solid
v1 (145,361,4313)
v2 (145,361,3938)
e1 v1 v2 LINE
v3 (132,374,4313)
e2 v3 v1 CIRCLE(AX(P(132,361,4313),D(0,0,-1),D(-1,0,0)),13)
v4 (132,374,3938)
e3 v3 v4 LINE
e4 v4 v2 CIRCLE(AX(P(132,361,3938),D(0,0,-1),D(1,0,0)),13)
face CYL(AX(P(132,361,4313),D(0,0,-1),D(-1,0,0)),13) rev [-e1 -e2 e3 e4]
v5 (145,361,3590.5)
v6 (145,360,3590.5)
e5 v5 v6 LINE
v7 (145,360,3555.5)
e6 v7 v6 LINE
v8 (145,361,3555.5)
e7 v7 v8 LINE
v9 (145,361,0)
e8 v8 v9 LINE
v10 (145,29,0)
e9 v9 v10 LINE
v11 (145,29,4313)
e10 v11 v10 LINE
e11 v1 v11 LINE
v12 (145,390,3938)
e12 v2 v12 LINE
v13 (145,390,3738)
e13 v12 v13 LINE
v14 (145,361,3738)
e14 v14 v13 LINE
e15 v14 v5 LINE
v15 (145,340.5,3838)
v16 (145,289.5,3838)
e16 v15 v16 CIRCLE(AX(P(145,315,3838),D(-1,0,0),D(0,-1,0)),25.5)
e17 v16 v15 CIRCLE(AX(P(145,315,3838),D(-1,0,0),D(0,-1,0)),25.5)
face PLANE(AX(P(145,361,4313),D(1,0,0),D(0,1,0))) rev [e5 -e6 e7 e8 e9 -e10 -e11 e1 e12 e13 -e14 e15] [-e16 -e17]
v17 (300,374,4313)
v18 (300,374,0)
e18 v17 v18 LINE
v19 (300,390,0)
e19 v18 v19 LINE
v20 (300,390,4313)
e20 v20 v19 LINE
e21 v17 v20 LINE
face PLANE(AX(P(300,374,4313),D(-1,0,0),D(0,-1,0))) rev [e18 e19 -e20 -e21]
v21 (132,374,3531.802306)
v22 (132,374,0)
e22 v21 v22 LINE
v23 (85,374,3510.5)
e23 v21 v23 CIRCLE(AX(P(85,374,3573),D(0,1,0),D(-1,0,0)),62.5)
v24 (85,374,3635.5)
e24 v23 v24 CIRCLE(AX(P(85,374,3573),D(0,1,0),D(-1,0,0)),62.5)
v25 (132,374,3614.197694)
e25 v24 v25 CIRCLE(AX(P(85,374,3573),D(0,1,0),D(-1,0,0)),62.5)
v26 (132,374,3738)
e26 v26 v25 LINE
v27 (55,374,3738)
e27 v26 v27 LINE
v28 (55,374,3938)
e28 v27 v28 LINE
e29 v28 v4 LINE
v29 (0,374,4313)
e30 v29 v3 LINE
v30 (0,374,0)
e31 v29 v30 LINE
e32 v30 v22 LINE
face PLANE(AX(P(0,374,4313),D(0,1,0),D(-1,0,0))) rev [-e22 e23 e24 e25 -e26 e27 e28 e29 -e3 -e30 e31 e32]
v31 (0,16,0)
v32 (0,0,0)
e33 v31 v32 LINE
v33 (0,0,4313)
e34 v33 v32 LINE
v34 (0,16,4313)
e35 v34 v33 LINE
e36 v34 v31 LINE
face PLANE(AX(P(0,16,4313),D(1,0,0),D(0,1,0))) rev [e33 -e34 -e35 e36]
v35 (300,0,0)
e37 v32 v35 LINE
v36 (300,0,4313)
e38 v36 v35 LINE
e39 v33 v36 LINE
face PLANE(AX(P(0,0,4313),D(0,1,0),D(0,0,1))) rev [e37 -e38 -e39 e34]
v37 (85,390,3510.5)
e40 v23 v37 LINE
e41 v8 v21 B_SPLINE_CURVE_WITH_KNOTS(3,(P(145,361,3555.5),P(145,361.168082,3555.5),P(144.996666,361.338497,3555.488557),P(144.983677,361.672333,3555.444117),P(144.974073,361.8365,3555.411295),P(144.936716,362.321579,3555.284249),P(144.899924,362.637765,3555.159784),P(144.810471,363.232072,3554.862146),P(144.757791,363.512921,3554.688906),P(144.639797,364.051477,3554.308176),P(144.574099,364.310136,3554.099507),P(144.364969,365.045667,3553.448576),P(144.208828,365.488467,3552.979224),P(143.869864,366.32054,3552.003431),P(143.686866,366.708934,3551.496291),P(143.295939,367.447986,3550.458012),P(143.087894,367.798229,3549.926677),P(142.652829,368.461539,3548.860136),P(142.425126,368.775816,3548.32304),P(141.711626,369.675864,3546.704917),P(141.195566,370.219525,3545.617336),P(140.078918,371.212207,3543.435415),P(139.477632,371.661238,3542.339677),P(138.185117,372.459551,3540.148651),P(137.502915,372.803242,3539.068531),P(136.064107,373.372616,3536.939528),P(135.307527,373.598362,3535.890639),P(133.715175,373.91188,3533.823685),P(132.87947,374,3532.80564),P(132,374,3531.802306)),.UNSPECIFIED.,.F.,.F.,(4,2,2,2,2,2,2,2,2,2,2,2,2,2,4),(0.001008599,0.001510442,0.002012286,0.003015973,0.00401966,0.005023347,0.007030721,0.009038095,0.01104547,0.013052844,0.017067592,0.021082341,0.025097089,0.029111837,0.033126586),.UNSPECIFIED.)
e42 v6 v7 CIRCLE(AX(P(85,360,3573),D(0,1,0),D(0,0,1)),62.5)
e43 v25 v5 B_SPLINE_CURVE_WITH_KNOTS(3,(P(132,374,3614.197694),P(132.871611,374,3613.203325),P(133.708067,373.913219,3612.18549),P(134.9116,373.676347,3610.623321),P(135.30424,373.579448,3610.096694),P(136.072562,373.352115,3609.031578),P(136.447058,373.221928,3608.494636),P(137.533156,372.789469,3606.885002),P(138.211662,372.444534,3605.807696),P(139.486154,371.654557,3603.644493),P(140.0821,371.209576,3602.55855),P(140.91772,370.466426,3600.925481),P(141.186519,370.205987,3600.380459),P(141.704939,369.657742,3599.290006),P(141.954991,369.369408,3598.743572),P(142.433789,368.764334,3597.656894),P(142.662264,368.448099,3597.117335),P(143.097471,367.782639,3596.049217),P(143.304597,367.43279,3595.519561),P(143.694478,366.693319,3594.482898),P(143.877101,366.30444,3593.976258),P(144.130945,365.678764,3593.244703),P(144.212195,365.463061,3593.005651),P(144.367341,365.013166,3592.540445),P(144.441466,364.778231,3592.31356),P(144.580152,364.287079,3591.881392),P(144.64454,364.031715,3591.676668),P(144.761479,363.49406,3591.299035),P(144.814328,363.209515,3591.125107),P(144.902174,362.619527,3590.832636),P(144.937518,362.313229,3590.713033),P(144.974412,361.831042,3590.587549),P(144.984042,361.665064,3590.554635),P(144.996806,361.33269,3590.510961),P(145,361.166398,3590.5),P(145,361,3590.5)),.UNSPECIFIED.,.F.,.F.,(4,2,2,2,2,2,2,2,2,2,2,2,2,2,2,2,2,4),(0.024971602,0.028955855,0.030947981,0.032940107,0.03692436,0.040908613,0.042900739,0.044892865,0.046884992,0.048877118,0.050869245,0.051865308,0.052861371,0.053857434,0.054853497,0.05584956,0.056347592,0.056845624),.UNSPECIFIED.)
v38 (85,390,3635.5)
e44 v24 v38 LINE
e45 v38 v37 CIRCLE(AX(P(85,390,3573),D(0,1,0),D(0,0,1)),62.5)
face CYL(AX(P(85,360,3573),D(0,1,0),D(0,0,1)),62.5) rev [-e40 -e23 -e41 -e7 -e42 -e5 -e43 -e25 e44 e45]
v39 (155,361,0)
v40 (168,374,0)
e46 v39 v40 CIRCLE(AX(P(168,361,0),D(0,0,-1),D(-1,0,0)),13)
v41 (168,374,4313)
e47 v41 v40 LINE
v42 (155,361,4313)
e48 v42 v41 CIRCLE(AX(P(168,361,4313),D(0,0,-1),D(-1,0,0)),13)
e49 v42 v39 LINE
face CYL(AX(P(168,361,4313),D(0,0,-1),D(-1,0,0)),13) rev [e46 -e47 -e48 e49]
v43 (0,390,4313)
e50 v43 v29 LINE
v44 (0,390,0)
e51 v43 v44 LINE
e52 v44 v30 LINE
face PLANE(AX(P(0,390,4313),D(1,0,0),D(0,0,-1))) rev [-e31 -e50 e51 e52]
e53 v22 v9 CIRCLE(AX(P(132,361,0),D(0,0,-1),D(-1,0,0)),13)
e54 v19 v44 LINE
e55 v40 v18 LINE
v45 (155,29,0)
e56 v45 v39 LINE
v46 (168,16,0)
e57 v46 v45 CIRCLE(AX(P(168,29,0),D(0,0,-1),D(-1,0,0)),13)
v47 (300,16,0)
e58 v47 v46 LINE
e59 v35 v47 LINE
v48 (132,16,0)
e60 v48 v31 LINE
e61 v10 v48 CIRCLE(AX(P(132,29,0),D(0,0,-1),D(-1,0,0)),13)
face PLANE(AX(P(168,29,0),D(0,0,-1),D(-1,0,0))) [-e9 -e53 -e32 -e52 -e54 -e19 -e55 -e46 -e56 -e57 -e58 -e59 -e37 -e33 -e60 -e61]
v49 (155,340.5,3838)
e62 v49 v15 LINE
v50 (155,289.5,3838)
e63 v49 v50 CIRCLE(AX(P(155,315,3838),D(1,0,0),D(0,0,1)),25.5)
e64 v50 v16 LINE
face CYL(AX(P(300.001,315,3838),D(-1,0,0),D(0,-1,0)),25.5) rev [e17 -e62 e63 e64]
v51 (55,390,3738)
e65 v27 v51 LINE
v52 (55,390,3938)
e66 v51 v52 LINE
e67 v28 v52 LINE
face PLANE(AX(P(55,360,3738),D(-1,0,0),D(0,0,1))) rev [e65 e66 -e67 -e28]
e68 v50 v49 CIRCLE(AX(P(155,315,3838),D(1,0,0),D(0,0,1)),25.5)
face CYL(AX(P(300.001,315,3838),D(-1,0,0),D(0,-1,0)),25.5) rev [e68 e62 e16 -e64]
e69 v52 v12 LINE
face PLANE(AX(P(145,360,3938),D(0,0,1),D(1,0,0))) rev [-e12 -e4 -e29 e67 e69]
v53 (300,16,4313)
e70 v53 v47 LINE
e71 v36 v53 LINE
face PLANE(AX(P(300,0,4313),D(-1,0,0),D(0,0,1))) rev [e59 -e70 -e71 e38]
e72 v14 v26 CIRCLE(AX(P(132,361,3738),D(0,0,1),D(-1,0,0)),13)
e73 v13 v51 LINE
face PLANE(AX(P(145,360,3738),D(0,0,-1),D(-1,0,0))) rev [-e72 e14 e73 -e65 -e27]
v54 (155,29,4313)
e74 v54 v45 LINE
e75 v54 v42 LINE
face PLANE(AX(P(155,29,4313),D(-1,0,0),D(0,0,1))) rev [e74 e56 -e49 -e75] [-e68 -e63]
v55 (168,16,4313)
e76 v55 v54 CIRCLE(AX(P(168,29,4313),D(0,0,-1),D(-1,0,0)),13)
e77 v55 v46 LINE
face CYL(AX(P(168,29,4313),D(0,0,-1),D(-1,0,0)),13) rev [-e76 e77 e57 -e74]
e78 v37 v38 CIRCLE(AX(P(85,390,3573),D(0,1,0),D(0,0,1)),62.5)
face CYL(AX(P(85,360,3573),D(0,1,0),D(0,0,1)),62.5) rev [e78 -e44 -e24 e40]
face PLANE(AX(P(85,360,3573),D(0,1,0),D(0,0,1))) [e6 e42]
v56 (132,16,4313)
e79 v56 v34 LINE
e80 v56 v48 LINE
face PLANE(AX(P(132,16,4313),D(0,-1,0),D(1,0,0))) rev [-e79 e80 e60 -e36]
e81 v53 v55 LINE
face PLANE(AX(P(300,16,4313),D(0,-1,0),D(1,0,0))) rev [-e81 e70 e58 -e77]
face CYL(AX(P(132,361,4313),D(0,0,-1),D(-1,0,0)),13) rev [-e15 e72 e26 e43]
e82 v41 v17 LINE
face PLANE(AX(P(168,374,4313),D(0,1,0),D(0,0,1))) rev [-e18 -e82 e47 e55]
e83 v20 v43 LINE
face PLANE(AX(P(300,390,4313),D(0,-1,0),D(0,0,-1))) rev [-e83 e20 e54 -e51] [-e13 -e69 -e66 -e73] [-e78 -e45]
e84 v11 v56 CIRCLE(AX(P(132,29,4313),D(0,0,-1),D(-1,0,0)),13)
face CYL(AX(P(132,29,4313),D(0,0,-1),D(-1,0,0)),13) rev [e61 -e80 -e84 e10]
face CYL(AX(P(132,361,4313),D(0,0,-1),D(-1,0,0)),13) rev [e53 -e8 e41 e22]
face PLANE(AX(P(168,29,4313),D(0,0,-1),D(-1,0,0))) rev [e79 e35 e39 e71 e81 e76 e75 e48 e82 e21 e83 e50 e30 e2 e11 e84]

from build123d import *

# Parameters (mm, degrees)
BOSS_EXTRUDE1_DEPTH = 4313
SKETCH2_R           = 62.5
SKETCH2_W           = 90
SKETCH2_H           = 200
CUT_EXTRUDE1_DEPTH  = 30
CUT_EXTRUDE2_REACH  = 4335.37
SKETCH3_R           = 25.5


with BuildPart() as part:
    # Sketch1 → Boss-Extrude1 (new body)
    with BuildSketch(Plane.XY):
        with BuildLine():
            Line((0, 0), (300, 0))
            Line((300, 0), (300, 16))
            Line((300, 16), (168, 16))
            ThreePointArc((168, 16), (158.807611845, 19.807611845), (155, 29))
            Line((155, 29), (155, 361))
            ThreePointArc((155, 361), (158.807611845, 370.192388155), (168, 374))
            Line((168, 374), (300, 374))
            Line((300, 374), (300, 390))
            Line((300, 390), (0, 390))
            Line((0, 390), (0, 374))
            Line((0, 374), (132, 374))
            ThreePointArc((132, 374), (141.192388155, 370.192388155), (145, 361))
            Line((145, 361), (145, 29))
            ThreePointArc((145, 29), (141.192388155, 19.807611845), (132, 16))
            Line((132, 16), (0, 16))
            Line((0, 16), (0, 0))
        make_face()
    extrude(amount=BOSS_EXTRUDE1_DEPTH)

    # Sketch2 → Cut-Extrude1 (cut)
    with BuildSketch(Plane(origin=(0, 390, 0), x_dir=(1, 0, 0), z_dir=(0, 1, 0))):
        with Locations(Location((85, -3573, 0), (0, 0, 270))):
            Circle(SKETCH2_R)
        with Locations((100, -3838)):
            Rectangle(SKETCH2_W, SKETCH2_H)
    extrude(amount=-CUT_EXTRUDE1_DEPTH, mode=Mode.SUBTRACT)

    # Sketch3 → Cut-Extrude2 (cut, up to next)
    with BuildSketch(Plane.ZY.offset(-145), mode=Mode.PRIVATE) as cut_extrude2_sk1:
        with Locations(Location((3838, 315, 0), (0, 0, 270))):
            Circle(SKETCH3_R)
    cut_extrude2_tool1 = extrude(cut_extrude2_sk1.sketch, amount=-CUT_EXTRUDE2_REACH, mode=Mode.PRIVATE) & part.part
    add(cut_extrude2_tool1.solids().sort_by_distance((145, 315, 3838))[0], mode=Mode.SUBTRACT)


solid = part.part
